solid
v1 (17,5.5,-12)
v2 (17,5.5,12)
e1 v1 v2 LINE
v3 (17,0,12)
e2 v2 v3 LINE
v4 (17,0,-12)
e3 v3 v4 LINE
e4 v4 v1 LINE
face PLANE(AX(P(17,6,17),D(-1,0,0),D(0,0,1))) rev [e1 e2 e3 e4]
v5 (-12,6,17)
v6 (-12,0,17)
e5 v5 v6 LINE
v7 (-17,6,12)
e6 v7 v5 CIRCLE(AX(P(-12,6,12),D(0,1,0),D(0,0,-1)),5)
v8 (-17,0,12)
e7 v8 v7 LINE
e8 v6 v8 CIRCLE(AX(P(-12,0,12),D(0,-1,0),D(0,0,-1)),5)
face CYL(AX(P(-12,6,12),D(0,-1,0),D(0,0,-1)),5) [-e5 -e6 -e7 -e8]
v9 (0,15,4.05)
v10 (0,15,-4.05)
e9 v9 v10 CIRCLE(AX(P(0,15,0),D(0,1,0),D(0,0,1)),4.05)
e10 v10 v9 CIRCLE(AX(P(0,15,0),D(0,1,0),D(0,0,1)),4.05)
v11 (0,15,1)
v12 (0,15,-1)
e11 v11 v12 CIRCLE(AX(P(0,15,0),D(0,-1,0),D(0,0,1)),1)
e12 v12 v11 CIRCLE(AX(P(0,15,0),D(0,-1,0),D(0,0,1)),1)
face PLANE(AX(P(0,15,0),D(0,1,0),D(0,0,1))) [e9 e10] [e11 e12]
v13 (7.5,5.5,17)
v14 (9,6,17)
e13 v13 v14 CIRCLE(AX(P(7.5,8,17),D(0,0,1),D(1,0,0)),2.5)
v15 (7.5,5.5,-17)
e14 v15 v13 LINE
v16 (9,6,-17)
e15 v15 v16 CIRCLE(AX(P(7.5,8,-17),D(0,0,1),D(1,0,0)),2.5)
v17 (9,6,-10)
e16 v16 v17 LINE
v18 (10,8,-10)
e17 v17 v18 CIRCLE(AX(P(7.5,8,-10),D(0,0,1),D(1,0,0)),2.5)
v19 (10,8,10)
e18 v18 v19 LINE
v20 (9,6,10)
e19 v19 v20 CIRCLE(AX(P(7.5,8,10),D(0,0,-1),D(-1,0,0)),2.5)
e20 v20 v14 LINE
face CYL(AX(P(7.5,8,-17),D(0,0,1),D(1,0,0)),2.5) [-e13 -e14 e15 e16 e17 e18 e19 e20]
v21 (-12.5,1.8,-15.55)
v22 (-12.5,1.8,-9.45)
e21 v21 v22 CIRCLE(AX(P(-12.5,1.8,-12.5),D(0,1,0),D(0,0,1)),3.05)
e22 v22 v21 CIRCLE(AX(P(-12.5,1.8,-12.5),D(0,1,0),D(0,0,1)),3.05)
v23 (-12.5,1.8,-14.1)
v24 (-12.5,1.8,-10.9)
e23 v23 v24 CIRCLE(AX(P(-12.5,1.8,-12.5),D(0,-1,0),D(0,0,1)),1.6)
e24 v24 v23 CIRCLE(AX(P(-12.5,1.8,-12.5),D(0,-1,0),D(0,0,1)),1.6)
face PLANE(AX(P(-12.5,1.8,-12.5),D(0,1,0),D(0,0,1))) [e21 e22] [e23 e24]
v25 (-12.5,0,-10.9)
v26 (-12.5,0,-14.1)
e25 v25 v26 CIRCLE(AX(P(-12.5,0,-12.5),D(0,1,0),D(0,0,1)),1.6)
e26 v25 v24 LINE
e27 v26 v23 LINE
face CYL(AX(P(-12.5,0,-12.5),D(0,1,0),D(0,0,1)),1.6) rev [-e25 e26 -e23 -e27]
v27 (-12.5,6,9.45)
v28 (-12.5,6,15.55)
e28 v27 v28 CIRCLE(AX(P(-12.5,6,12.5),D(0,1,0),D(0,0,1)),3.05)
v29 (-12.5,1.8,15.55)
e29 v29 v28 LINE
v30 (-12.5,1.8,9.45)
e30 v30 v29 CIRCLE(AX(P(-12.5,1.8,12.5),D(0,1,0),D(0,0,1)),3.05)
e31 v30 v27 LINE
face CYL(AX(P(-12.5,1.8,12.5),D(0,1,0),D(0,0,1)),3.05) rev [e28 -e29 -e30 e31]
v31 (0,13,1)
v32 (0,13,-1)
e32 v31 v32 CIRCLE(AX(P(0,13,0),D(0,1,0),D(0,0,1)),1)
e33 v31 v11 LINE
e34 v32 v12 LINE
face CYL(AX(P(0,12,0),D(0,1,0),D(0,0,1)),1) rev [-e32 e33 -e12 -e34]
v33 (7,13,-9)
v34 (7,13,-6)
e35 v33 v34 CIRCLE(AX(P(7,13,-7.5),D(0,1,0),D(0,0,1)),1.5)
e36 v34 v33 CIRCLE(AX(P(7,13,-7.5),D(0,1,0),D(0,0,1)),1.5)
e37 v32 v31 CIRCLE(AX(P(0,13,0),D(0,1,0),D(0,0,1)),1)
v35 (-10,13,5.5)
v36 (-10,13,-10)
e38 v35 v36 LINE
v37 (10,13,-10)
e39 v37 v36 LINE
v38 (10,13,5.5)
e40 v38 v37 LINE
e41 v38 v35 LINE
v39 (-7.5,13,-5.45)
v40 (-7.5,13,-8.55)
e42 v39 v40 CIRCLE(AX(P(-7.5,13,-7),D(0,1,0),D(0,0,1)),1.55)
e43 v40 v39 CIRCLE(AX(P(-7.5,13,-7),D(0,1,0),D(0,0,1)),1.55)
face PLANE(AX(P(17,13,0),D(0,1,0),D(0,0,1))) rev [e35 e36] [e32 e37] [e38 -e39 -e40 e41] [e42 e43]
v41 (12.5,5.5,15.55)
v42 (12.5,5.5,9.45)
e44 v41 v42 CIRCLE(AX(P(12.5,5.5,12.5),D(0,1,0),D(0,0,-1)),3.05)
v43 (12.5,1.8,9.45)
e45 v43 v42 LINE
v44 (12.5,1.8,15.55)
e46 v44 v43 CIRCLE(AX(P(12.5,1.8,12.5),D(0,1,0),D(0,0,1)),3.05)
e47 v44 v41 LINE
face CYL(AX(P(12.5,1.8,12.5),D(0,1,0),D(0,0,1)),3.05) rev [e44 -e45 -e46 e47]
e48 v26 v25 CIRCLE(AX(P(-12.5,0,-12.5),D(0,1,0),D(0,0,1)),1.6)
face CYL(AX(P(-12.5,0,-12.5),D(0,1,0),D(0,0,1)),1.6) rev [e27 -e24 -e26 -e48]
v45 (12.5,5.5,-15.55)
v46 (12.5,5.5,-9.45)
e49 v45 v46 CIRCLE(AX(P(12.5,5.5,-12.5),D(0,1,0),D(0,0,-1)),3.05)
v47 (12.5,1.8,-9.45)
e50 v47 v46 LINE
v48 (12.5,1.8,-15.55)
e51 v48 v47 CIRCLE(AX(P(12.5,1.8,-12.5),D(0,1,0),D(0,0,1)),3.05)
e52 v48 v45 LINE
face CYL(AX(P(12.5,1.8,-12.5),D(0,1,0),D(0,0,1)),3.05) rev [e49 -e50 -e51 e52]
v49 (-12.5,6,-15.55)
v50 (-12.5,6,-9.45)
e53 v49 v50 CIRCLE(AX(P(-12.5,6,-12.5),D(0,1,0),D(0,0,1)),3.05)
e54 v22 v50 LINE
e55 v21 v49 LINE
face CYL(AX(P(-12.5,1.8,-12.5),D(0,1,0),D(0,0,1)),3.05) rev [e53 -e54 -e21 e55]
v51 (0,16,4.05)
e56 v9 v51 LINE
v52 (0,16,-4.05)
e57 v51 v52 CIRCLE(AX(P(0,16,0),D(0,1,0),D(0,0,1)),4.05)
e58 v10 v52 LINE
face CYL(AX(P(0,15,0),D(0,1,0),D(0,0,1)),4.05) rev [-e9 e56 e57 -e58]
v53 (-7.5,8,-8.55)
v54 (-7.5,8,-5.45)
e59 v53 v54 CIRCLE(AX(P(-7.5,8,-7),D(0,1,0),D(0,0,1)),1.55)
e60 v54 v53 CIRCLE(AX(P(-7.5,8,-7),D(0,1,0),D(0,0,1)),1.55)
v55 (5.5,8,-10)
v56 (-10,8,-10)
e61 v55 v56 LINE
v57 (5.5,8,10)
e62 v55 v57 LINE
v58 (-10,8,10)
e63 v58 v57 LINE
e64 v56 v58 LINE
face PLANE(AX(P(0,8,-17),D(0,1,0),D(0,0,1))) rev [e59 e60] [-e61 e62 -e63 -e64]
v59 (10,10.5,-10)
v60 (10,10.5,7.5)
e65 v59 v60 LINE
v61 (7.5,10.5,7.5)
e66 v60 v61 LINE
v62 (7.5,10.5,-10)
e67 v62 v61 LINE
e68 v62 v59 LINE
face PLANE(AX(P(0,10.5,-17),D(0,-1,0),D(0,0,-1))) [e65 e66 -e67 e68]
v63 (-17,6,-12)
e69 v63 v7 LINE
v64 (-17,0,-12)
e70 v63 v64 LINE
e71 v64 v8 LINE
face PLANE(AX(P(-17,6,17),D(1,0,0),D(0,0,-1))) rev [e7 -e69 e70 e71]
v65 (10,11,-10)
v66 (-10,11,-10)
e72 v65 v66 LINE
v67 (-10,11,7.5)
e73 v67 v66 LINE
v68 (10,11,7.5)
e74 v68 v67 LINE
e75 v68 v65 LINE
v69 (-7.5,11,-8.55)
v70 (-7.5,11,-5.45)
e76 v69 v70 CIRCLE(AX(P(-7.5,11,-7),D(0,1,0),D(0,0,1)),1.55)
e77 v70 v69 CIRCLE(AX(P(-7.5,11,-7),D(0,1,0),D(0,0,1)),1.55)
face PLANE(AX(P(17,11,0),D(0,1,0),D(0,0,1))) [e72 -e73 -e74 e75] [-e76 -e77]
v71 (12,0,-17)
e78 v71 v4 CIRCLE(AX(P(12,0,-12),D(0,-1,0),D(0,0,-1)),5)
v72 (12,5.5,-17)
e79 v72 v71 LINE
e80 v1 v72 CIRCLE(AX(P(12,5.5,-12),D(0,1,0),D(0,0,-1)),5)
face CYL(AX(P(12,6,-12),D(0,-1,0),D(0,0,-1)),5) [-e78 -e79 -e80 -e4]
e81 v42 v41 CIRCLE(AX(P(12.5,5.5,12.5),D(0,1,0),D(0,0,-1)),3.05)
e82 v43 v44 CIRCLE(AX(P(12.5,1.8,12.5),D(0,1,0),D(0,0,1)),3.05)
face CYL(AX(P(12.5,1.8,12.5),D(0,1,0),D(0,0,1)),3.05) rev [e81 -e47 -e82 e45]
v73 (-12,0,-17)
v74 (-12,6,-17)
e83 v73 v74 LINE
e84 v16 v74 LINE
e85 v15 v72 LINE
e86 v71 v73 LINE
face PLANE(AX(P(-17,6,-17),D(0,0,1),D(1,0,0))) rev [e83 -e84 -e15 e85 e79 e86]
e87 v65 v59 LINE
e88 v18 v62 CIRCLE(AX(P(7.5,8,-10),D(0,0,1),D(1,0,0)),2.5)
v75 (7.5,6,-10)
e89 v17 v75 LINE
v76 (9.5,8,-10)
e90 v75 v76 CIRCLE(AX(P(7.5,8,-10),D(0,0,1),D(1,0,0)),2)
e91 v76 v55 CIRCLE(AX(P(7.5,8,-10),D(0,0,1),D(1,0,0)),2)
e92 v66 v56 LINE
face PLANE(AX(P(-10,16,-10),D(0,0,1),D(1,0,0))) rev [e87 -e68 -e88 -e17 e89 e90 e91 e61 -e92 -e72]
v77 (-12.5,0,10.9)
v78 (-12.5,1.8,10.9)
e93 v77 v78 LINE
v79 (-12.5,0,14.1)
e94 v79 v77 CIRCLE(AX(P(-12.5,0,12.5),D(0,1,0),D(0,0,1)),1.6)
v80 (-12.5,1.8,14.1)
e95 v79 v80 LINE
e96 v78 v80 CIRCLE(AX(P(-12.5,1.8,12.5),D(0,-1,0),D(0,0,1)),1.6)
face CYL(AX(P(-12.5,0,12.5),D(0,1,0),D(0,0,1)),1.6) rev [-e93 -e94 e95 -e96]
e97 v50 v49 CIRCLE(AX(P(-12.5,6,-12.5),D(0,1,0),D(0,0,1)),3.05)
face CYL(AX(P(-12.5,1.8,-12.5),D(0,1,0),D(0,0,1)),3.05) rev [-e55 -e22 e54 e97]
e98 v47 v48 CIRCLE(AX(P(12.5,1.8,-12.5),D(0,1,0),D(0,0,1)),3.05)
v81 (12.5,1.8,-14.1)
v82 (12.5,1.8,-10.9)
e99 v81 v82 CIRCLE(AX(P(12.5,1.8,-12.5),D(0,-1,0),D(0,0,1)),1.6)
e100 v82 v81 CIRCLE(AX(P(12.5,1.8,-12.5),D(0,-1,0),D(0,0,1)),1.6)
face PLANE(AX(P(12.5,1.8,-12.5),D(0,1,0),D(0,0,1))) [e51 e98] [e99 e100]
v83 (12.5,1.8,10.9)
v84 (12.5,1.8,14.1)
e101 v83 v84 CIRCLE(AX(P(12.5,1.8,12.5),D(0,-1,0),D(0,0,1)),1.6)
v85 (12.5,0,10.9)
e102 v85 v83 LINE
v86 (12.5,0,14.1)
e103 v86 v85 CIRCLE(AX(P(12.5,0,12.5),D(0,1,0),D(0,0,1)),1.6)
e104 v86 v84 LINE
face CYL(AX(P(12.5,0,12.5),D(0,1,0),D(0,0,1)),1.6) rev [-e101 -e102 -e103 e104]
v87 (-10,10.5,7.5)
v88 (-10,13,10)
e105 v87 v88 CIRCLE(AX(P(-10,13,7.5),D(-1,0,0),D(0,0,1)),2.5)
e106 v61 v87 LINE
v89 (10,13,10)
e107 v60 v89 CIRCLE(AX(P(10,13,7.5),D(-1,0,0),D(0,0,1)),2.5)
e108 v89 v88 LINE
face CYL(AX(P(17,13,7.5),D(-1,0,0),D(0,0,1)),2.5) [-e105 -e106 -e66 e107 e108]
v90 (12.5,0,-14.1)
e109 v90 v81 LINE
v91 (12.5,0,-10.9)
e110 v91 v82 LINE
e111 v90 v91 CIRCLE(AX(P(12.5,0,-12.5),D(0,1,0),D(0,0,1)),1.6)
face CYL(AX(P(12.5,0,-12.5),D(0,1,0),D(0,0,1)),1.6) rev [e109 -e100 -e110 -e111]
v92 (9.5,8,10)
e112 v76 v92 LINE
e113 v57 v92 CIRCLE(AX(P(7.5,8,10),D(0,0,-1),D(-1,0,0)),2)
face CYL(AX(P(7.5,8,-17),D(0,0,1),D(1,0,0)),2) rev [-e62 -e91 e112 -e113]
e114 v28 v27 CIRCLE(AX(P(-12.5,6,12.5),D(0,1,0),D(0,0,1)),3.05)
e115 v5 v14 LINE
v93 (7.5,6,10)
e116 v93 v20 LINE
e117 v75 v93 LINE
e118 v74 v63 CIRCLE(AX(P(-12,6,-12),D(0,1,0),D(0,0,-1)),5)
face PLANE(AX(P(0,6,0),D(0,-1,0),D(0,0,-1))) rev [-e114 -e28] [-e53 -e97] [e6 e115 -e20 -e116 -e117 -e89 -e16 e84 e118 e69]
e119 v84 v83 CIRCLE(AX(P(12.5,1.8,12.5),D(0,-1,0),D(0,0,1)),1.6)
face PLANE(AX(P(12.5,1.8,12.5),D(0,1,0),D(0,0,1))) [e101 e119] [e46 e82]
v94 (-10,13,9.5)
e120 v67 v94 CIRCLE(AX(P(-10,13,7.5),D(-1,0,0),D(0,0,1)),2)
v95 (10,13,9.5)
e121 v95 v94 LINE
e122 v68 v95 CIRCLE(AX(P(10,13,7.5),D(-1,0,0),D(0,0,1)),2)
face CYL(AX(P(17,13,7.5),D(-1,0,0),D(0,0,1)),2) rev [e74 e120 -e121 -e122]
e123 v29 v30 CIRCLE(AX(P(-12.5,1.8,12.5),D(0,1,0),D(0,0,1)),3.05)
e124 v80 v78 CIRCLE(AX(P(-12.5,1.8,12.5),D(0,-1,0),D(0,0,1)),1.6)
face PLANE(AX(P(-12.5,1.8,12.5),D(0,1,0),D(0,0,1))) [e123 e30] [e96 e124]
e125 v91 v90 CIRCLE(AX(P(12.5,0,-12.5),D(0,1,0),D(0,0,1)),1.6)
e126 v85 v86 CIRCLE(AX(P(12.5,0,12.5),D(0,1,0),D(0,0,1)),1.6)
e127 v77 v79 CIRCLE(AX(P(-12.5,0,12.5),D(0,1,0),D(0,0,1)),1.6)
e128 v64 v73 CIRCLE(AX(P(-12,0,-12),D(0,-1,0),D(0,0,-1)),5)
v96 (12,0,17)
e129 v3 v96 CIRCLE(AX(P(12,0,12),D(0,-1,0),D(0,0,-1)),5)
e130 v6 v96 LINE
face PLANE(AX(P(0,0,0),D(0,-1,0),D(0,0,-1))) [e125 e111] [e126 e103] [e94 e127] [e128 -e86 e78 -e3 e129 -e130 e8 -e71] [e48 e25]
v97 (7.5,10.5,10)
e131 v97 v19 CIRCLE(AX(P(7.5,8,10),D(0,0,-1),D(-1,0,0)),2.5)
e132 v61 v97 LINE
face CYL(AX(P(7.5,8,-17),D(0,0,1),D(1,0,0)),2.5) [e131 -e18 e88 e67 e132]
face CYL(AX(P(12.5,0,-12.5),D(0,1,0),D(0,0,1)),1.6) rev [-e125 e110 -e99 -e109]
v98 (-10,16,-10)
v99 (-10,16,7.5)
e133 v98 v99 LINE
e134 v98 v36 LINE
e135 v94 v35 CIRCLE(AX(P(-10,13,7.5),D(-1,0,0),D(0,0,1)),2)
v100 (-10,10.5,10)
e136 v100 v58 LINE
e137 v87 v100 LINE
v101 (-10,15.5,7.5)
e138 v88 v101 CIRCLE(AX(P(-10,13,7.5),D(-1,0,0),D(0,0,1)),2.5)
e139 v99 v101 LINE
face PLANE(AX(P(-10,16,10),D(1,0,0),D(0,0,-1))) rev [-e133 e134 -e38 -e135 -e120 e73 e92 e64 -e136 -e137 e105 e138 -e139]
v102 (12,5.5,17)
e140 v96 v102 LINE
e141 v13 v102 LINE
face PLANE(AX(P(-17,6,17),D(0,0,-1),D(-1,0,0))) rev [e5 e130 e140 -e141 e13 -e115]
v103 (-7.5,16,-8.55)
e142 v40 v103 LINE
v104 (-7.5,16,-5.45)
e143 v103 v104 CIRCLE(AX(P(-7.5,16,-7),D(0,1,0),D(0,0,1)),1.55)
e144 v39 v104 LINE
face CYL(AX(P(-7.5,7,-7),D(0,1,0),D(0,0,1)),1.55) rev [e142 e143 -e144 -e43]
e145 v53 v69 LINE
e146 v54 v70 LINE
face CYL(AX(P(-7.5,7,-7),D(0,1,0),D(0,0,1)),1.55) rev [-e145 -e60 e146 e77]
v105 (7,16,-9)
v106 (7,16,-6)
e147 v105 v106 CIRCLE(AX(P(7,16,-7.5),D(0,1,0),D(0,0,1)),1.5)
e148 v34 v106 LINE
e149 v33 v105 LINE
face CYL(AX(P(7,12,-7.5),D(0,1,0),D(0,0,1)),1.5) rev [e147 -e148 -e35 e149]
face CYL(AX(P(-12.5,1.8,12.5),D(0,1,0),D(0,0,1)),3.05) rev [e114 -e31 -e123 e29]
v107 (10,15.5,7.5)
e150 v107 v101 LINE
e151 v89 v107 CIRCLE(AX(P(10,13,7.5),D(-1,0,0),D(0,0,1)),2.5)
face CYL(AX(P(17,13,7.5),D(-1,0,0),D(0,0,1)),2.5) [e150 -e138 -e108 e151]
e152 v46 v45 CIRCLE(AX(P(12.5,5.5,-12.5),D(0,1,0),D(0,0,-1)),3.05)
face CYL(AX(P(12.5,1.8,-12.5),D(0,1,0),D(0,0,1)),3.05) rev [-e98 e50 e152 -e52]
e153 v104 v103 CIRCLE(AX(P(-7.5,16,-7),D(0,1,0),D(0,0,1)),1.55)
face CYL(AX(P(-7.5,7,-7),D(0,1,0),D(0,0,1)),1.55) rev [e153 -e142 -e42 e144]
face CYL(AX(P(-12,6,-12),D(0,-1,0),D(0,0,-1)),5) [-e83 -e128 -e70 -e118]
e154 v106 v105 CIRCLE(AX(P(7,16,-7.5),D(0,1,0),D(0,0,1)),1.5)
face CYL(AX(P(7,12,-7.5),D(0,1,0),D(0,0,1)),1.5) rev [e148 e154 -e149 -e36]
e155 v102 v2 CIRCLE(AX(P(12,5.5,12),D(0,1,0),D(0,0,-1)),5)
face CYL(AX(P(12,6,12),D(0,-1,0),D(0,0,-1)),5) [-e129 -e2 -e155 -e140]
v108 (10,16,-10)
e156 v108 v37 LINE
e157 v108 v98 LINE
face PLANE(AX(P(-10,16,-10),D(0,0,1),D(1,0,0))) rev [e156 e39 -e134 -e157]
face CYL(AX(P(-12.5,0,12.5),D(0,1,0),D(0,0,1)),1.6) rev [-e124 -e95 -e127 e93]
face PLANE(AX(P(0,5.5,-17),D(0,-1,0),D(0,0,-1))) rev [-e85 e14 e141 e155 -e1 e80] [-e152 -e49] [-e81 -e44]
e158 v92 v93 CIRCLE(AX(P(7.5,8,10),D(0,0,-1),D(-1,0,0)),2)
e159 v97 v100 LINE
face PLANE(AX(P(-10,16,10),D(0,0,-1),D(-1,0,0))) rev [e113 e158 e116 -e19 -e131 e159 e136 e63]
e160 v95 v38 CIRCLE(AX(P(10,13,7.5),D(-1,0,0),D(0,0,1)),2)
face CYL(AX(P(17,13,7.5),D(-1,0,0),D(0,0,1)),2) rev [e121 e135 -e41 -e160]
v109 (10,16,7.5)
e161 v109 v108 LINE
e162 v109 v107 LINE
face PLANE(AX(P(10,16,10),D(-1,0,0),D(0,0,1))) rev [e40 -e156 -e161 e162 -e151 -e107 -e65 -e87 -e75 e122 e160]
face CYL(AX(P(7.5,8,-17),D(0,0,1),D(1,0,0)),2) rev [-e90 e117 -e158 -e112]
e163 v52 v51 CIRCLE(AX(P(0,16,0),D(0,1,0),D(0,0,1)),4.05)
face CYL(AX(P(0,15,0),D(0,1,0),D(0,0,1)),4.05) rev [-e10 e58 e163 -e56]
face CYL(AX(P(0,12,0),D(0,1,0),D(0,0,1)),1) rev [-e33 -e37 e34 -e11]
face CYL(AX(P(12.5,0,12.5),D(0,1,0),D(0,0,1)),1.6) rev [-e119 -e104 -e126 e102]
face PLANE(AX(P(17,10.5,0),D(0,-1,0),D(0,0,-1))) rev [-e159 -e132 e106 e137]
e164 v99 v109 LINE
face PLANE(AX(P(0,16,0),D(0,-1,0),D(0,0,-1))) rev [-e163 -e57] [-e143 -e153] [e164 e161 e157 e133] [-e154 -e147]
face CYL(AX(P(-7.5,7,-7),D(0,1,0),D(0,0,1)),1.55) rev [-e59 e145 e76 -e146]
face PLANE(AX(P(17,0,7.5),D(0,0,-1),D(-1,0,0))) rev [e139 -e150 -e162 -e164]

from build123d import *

# Parameters (mm, degrees)
SKETCH1_W           = 34
SKETCH1_H           = 34
BOSS_EXTRUDE1_DEPTH = 6
SKETCH2_R           = 1.6
CUT_EXTRUDE1_DEPTH  = 6
SKETCH3_R           = 3.05
CUT_EXTRUDE2_DEPTH  = 4.2
SKETCH4_W           = 20
SKETCH4_H           = 20
BOSS_EXTRUDE2_DEPTH = 10
CUT_EXTRUDE4_DEPTH  = 42.243181255
CUT_EXTRUDE5_DEPTH  = 36.693136595
SKETCH7_R           = 1.5
CUT_EXTRUDE6_DEPTH  = 4
FILLET1_R           = 5
SKETCH8_R           = 1
CUT_EXTRUDE7_DEPTH  = 4
SKETCH9_R           = 4.05
CUT_EXTRUDE8_DEPTH  = 1
SKETCH10_R          = 1.55
CUT_EXTRUDE9_DEPTH  = 9


with BuildPart() as part:
    # Sketch1 → Boss-Extrude1 (new body)
    with BuildSketch(Plane(origin=(0, 0, 0), x_dir=(1, 0, 0), z_dir=(0, 1, 0))):
        Rectangle(SKETCH1_W, SKETCH1_H)
    extrude(amount=BOSS_EXTRUDE1_DEPTH)

    # Sketch2 → Cut-Extrude1 (cut)
    with BuildSketch(Plane(origin=(0, 6, 0), x_dir=(1, 0, 0), z_dir=(0, 1, 0))):
        with Locations(Location((-12.5, 12.5, 0), (0, 0, 270))):
            Circle(SKETCH2_R)
        with Locations(Location((12.5, 12.5, 0), (0, 0, 270))):
            Circle(SKETCH2_R)
        with Locations(Location((12.5, -12.5, 0), (0, 0, 270))):
            Circle(SKETCH2_R)
        with Locations(Location((-12.5, -12.5, 0), (0, 0, 270))):
            Circle(SKETCH2_R)
    extrude(amount=-CUT_EXTRUDE1_DEPTH, mode=Mode.SUBTRACT)

    # Sketch3 → Cut-Extrude2 (cut)
    with BuildSketch(Plane(origin=(0, 6, 0), x_dir=(1, 0, 0), z_dir=(0, 1, 0))):
        with Locations(Location((-12.5, 12.5, 0), (0, 0, 270))):
            Circle(SKETCH3_R)
        with Locations(Location((12.5, 12.5, 0), (0, 0, 270))):
            Circle(SKETCH3_R)
        with Locations(Location((12.5, -12.5, 0), (0, 0, 270))):
            Circle(SKETCH3_R)
        with Locations(Location((-12.5, -12.5, 0), (0, 0, 270))):
            Circle(SKETCH3_R)
    extrude(amount=-CUT_EXTRUDE2_DEPTH, mode=Mode.SUBTRACT)

    # Sketch4 → Boss-Extrude2 (add)
    with BuildSketch(Plane(origin=(0, 6, 0), x_dir=(1, 0, 0), z_dir=(0, 1, 0))):
        Rectangle(SKETCH4_W, SKETCH4_H)
    extrude(amount=BOSS_EXTRUDE2_DEPTH)

    # Sketch5 → Cut-Extrude4 (cut, through all)
    with BuildSketch(Plane.XY.offset(17)):
        with BuildLine():
            Line((-10, 6), (7.5, 6))
            ThreePointArc((7.5, 6), (8.914213562, 9.414213562), (5.5, 8))
            Line((5.5, 8), (-10, 8))
            Line((-10, 8), (-10, 6))
        make_face()
        with BuildLine():
            Line((10, 10.5), (7.5, 10.5))
            ThreePointArc((7.5, 10.5), (9.267766953, 9.767766953), (10, 8))
            Line((10, 8), (10, 10.5))
        make_face()
        with BuildLine():
            Line((10, 6), (10, 8))
            ThreePointArc((10, 8), (9.736067977, 6.881966011), (9, 6))
            Line((9, 6), (10, 6))
        make_face()
        with BuildLine():
            Line((17, 6), (10, 6))
            Line((10, 6), (9, 6))
            ThreePointArc((9, 6), (8.290569415, 5.628291755), (7.5, 5.5))
            Line((7.5, 5.5), (17, 5.5))
            Line((17, 5.5), (17, 6))
        make_face()
    extrude(amount=-CUT_EXTRUDE4_DEPTH, mode=Mode.SUBTRACT)

    # Sketch6 → Cut-Extrude5 (cut, through all)
    with BuildSketch(Plane.ZY.offset(10)):
        with BuildLine():
            ThreePointArc((10, 13), (9.267766953, 11.232233047), (7.5, 10.5))
            Line((7.5, 10.5), (10, 10.5))
            Line((10, 10.5), (10, 13))
        make_face()
        with BuildLine():
            ThreePointArc((7.5, 15.5), (9.267766953, 14.767766953), (10, 13))
            Line((10, 13), (10, 16))
            Line((10, 16), (7.5, 16))
            Line((7.5, 16), (7.5, 15.5))
        make_face()
        with BuildLine():
            Line((-10, 13), (-10, 11))
            Line((-10, 11), (7.5, 11))
            ThreePointArc((7.5, 11), (8.914213562, 14.414213562), (5.5, 13))
            Line((5.5, 13), (-10, 13))
        make_face()
    extrude(amount=-CUT_EXTRUDE5_DEPTH, mode=Mode.SUBTRACT)

    # Sketch7 → Cut-Extrude6 (cut)
    with BuildSketch(Plane(origin=(0, 16, 0), x_dir=(1, 0, 0), z_dir=(0, 1, 0))):
        with Locations(Location((7, 7.5, 0), (0, 0, 270))):
            Circle(SKETCH7_R)
    extrude(amount=-CUT_EXTRUDE6_DEPTH, mode=Mode.SUBTRACT)

    # Fillet1
    fillet1_edges = [part.edges().sort_by_distance(p)[0] for p in [
        (17, 2.75, 17),
        (17, 2.75, -17),
        (-17, 3, 17),
        (-17, 3, -17),
    ]]
    fillet(fillet1_edges, radius=FILLET1_R)

    # Sketch8 → Cut-Extrude7 (cut)
    with BuildSketch(Plane(origin=(0, 16, 0), x_dir=(1, 0, 0), z_dir=(0, 1, 0))):
        with Locations(Location((0, 0, 0), (0, 0, 270))):
            Circle(SKETCH8_R)
    extrude(amount=-CUT_EXTRUDE7_DEPTH, mode=Mode.SUBTRACT)

    # Sketch9 → Cut-Extrude8 (cut)
    with BuildSketch(Plane(origin=(0, 16, 0), x_dir=(1, 0, 0), z_dir=(0, 1, 0))):
        with Locations(Location((0, 0, 0), (0, 0, 270))):
            Circle(SKETCH9_R)
    extrude(amount=-CUT_EXTRUDE8_DEPTH, mode=Mode.SUBTRACT)

    # Sketch10 → Cut-Extrude9 (cut)
    with BuildSketch(Plane(origin=(0, 16, 0), x_dir=(1, 0, 0), z_dir=(0, 1, 0))):
        with Locations(Location((-7.5, 7, 0), (0, 0, 270))):
            Circle(SKETCH10_R)
    extrude(amount=-CUT_EXTRUDE9_DEPTH, mode=Mode.SUBTRACT)


solid = part.part
